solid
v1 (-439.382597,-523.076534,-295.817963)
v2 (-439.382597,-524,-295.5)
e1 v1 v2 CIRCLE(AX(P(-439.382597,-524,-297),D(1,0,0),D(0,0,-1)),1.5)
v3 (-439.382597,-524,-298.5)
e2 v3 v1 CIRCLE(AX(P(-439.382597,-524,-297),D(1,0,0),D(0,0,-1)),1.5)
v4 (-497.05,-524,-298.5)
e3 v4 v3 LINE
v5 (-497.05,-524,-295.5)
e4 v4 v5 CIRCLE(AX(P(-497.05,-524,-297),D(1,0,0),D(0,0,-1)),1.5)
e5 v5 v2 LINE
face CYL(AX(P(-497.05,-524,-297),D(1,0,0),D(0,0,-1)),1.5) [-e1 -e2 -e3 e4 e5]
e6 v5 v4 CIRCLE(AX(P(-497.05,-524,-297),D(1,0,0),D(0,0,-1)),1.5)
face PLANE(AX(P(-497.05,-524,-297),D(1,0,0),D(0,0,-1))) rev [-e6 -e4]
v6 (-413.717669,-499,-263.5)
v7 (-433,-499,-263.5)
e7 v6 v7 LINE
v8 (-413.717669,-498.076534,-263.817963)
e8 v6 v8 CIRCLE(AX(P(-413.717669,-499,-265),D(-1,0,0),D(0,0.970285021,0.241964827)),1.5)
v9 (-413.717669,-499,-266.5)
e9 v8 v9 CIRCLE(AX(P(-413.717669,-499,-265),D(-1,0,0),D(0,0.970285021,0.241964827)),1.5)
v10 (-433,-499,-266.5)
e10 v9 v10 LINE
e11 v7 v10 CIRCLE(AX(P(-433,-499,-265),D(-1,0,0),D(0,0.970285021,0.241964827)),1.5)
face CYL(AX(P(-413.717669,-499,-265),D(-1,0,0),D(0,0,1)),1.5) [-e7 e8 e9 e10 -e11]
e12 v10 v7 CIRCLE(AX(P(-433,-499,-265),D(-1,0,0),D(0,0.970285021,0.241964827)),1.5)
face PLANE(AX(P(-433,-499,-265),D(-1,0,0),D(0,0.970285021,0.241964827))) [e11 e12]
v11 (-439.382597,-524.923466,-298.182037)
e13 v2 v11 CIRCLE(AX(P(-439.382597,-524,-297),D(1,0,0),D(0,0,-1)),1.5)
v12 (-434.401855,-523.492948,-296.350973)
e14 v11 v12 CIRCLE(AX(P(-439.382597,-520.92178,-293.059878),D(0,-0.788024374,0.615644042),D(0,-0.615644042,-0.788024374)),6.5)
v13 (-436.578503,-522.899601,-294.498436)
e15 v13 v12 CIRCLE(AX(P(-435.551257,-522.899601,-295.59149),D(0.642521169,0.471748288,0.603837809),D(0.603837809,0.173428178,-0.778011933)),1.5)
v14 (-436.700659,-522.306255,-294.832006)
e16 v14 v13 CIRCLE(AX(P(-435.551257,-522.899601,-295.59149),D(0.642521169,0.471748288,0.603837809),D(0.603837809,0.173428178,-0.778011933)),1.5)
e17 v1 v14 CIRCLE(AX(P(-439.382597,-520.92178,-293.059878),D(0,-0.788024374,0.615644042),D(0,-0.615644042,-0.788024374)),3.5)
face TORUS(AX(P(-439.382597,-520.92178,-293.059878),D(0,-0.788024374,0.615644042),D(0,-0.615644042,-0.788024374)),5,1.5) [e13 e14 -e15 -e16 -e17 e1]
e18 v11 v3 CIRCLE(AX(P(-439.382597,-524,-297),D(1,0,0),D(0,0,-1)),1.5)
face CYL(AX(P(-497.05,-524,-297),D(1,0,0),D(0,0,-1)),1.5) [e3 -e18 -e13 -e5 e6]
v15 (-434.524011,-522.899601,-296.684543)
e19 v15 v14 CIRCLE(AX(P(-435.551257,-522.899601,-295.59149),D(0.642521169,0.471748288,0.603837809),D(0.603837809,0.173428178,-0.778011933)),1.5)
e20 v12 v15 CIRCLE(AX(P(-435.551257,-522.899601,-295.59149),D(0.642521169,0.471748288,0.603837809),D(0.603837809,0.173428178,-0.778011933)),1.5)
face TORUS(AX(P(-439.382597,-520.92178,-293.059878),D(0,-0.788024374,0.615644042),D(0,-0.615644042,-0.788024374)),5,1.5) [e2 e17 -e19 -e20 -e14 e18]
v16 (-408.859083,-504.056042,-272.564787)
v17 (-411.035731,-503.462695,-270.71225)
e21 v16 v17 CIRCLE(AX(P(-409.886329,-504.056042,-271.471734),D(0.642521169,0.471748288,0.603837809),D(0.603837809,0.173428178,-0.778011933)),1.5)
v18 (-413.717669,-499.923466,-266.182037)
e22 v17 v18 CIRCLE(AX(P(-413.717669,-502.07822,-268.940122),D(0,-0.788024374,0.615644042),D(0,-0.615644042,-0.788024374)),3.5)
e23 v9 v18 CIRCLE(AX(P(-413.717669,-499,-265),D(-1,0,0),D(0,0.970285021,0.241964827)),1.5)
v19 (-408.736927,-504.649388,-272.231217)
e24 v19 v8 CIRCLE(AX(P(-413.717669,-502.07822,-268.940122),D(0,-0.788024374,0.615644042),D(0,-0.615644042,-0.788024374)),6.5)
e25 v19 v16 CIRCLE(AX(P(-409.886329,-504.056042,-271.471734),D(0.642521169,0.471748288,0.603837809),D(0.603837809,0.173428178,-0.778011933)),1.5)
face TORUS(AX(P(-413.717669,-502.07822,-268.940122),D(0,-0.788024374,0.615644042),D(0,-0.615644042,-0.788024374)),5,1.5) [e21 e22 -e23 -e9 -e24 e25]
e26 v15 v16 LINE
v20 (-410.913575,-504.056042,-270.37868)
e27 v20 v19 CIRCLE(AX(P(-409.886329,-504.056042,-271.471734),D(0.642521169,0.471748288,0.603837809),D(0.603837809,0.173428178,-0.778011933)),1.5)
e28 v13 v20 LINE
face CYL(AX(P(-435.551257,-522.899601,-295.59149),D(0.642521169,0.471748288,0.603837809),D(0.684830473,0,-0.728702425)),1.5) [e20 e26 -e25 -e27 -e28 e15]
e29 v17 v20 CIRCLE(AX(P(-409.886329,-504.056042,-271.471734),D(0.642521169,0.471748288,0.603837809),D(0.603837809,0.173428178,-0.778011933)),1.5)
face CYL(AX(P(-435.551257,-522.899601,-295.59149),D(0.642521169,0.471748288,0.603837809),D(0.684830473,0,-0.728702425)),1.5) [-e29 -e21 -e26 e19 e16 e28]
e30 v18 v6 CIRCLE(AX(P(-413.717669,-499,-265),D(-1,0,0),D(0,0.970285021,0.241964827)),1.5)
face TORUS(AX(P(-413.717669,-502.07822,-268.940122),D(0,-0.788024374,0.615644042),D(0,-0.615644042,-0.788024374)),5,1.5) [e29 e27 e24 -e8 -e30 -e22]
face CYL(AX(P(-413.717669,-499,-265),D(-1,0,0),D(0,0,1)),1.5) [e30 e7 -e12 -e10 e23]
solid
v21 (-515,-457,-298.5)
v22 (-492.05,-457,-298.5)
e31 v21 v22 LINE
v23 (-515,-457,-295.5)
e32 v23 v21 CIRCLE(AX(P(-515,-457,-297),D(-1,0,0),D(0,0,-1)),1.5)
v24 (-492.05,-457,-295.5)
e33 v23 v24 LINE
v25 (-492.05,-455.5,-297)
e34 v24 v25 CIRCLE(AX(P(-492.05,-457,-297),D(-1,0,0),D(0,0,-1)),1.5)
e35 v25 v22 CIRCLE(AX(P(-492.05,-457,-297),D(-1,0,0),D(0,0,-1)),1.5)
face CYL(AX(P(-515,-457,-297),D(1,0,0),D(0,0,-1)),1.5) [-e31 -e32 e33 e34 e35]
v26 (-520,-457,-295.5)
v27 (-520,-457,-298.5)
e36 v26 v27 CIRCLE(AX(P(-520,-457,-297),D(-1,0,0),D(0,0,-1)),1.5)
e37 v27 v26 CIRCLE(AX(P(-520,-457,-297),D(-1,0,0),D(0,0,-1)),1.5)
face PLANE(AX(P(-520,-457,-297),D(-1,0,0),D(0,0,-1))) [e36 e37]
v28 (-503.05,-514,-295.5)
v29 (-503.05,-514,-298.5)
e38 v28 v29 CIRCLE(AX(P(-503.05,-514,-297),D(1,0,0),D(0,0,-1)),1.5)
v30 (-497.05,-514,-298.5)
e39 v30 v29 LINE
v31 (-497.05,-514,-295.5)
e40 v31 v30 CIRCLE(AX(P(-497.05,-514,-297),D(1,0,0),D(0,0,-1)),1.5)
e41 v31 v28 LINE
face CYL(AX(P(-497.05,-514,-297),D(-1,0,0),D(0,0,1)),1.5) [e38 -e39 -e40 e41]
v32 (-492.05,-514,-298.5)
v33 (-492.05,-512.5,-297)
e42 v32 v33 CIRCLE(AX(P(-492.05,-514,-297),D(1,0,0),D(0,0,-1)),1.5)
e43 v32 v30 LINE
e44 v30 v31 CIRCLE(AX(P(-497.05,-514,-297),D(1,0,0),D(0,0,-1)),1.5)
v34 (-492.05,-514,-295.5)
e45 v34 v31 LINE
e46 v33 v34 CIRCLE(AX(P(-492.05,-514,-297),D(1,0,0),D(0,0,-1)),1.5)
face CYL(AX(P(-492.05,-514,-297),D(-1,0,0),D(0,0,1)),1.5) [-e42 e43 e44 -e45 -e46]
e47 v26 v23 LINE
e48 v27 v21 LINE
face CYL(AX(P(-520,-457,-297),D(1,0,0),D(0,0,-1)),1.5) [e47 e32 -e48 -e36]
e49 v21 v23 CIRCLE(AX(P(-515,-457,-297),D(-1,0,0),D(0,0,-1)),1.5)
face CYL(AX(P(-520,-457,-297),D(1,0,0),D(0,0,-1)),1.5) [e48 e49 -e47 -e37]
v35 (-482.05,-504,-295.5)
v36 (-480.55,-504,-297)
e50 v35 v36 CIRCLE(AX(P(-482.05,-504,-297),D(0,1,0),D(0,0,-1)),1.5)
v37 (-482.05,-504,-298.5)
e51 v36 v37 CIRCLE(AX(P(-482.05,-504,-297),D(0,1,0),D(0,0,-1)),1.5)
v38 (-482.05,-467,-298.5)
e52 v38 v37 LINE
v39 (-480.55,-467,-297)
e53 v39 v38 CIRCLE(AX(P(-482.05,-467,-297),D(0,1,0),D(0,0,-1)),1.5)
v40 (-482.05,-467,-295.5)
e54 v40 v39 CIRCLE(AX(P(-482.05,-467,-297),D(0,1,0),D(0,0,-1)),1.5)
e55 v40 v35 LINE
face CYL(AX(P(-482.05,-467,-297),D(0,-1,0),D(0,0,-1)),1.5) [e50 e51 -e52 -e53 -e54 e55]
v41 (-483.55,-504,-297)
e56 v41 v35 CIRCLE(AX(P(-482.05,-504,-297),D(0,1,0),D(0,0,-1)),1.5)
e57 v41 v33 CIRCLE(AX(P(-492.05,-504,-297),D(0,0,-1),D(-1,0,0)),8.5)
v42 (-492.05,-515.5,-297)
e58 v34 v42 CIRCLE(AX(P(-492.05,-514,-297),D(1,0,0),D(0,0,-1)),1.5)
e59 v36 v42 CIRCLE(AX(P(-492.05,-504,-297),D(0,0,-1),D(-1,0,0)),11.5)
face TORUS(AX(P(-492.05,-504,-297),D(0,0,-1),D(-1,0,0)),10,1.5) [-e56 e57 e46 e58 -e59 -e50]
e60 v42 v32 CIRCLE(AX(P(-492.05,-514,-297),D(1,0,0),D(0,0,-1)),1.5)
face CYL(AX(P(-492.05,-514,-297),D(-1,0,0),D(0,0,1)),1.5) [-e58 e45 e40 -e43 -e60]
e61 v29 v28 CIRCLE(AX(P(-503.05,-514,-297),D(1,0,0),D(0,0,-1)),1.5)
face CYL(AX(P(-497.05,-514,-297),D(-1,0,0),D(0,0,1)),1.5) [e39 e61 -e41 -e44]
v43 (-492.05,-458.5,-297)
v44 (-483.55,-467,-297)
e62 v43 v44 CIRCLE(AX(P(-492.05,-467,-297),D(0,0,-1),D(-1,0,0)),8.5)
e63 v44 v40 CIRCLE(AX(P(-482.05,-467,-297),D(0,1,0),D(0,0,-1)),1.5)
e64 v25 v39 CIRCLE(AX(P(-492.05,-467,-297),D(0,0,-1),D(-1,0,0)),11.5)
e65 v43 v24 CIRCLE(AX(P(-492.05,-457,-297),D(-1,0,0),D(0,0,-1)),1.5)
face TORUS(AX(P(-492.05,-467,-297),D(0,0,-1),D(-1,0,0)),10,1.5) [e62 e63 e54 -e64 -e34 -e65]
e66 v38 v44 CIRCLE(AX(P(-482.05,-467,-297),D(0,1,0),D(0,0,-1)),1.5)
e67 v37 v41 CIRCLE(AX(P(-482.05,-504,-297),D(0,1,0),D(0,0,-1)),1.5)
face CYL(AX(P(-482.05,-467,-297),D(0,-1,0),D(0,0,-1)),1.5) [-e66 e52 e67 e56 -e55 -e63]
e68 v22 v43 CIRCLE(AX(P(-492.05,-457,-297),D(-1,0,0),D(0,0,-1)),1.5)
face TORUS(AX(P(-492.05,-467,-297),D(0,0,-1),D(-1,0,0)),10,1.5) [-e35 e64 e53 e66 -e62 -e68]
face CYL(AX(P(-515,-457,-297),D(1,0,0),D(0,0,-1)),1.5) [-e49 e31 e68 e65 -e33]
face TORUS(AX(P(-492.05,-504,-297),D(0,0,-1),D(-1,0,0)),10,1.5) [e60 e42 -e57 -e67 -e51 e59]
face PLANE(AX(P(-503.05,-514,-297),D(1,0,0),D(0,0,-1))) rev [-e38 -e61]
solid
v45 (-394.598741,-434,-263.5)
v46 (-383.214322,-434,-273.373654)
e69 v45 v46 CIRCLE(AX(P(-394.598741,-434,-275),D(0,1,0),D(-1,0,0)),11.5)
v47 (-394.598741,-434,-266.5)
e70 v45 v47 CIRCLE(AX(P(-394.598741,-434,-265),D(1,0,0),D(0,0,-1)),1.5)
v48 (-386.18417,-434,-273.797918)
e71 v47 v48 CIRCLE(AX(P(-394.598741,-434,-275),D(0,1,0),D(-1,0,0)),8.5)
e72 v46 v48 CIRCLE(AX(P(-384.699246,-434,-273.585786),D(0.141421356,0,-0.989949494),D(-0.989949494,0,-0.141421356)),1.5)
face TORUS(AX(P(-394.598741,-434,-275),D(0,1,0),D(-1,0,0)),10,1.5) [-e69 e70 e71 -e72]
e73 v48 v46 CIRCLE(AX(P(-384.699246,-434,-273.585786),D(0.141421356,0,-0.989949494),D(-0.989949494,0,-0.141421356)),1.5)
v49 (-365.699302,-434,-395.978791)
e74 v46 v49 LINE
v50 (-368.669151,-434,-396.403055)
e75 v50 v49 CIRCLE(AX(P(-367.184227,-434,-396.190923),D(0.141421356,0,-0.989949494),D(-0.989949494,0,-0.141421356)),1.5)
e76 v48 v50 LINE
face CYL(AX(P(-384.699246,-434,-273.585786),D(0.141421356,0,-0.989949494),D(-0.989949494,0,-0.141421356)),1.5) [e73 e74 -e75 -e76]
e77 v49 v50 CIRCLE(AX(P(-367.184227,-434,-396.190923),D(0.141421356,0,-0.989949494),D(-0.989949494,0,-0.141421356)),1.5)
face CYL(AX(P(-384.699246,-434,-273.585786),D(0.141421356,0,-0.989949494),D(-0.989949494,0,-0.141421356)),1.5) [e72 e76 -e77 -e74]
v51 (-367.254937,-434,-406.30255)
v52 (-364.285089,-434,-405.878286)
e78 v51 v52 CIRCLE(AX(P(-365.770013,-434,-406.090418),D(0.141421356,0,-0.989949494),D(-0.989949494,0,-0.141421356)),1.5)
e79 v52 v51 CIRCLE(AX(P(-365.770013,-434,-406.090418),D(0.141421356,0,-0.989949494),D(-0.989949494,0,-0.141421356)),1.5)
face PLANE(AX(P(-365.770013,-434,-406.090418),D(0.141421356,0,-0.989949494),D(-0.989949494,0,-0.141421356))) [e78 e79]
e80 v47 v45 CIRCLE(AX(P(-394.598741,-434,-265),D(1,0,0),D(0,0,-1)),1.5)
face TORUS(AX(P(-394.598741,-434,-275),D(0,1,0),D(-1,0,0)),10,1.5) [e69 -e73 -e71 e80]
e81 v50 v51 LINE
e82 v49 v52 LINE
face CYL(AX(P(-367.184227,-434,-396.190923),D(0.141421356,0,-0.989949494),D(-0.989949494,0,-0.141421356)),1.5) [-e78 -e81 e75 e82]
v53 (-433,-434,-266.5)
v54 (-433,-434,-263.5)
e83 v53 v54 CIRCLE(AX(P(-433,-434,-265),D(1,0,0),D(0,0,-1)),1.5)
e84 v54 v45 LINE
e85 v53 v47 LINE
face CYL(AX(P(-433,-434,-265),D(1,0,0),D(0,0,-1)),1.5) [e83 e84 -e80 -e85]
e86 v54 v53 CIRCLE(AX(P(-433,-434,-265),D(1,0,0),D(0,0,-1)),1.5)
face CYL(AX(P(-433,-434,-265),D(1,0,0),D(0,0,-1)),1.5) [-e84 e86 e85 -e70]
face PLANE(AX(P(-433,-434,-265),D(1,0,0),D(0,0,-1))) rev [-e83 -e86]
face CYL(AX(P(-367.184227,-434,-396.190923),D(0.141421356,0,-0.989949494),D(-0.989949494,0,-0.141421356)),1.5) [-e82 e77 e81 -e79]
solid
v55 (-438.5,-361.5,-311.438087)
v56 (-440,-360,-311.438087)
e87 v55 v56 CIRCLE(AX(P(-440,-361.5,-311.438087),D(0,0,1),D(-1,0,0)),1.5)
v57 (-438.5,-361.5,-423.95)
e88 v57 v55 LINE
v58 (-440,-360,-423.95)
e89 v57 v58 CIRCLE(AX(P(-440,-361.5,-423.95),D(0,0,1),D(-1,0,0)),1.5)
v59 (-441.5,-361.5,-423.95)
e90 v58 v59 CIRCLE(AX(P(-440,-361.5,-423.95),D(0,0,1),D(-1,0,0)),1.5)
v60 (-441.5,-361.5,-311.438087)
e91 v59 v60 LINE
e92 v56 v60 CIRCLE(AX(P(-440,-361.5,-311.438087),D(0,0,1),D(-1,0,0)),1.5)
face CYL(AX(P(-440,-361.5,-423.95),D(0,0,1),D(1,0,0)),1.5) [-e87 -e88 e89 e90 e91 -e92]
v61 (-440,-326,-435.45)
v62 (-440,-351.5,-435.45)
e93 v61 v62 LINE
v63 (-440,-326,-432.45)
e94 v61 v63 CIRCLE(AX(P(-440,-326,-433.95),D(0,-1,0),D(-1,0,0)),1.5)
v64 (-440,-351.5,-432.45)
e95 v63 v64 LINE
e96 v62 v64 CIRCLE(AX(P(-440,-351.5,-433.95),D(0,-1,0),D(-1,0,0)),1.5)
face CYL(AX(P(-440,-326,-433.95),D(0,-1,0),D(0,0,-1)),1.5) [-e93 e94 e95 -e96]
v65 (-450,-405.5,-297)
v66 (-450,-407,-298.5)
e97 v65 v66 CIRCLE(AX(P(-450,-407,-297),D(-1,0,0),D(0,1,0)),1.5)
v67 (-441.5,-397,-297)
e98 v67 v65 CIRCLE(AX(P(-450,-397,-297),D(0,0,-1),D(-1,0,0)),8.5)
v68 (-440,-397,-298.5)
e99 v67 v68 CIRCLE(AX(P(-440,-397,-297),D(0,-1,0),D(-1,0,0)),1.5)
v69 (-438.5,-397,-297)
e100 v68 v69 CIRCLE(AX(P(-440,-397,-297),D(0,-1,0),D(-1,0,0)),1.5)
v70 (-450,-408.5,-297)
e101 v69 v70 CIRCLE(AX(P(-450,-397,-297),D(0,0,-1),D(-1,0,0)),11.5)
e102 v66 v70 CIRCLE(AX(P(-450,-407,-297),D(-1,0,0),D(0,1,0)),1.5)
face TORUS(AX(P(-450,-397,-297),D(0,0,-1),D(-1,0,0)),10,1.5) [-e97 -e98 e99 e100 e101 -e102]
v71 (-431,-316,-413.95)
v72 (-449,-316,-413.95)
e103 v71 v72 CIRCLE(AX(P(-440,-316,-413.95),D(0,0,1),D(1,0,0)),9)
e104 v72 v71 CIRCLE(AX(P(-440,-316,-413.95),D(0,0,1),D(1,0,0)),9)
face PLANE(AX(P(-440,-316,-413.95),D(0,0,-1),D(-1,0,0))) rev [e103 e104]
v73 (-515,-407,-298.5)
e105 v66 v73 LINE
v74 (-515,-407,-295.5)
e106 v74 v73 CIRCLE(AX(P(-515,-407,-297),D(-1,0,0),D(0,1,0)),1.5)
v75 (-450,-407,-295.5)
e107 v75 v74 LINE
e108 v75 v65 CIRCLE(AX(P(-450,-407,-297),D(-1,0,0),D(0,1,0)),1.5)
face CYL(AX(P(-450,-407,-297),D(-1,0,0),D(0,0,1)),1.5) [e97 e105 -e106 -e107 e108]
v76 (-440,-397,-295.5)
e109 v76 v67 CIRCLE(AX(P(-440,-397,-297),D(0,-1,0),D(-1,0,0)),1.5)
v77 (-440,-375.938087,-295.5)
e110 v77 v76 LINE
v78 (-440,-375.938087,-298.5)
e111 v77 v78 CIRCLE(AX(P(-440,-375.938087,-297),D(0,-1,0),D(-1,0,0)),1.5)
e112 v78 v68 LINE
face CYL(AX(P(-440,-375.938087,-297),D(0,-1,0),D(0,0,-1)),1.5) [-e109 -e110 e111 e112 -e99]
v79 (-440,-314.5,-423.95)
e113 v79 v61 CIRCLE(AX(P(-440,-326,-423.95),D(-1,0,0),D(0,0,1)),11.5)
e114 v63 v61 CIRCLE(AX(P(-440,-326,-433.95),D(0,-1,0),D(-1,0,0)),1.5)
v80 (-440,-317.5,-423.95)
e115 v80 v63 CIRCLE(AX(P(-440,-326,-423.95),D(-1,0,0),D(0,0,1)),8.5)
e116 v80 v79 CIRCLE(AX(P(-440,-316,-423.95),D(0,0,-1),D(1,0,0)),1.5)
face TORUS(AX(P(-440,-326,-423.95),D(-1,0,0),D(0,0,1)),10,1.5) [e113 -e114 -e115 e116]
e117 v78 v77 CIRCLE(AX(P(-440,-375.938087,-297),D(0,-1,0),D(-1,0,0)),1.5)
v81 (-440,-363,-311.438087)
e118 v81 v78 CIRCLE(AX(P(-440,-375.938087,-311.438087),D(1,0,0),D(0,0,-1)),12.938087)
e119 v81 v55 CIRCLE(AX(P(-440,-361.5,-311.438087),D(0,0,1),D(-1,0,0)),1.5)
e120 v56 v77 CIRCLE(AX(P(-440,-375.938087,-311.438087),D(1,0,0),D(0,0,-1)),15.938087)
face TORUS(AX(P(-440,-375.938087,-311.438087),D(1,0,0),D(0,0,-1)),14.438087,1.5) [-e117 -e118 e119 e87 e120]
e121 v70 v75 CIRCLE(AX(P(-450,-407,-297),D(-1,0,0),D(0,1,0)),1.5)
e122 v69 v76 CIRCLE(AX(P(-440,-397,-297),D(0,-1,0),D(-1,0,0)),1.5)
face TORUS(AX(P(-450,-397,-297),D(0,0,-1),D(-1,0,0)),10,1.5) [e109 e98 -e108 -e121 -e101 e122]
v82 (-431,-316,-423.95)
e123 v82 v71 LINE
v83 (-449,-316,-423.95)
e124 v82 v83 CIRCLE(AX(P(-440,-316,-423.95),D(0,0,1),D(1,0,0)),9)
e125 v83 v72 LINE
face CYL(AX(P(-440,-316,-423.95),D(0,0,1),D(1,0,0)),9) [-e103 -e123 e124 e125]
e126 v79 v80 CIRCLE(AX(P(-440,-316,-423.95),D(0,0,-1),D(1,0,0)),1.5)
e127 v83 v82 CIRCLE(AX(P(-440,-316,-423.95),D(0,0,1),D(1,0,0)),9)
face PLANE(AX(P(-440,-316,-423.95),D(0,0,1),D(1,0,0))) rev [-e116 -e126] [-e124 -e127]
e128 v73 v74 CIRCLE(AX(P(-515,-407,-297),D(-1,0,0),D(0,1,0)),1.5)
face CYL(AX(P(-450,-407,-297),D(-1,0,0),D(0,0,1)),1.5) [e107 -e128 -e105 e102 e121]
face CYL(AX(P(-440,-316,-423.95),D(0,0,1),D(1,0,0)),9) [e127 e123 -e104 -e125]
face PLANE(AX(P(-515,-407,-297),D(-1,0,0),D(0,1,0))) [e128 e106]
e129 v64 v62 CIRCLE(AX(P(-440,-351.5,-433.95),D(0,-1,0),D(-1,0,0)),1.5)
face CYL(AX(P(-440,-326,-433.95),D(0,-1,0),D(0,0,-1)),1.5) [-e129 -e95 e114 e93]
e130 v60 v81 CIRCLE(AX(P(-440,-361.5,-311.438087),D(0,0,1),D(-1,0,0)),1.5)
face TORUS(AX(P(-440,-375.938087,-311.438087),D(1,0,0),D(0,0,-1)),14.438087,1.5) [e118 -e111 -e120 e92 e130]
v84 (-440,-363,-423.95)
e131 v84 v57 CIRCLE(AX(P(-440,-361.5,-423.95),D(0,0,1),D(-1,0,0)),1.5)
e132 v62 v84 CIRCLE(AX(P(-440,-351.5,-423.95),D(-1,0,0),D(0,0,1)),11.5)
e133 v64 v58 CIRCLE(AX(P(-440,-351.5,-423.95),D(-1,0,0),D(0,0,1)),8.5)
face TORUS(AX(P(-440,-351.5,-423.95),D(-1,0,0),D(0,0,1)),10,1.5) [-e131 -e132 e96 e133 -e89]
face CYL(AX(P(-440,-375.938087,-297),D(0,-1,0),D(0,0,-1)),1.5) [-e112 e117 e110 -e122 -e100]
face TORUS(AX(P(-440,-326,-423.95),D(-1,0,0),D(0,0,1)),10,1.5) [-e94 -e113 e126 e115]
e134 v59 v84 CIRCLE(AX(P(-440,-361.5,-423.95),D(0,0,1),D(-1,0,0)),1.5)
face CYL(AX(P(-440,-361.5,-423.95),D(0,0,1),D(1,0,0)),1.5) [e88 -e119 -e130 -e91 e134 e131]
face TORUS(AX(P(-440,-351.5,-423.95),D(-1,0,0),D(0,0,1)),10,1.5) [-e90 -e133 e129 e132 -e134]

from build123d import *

# Parameters (mm, degrees)
SWEEP1_PROFILE_R    = 1.5
SWEEP2_PROFILE_R    = 1.5
SWEEP3_PROFILE_R    = 1.5
SWEEP4_PROFILE_R    = 1.5
SKETCH55_R          = 9
BOSS_EXTRUDE1_DEPTH = 10


with BuildPart() as part:
    # Sweep1: sweep along a curve in space
    with BuildLine() as sweep1_path:
        Line((-433, -499, -265), (-413.717668682, -499, -265))
        ThreePointArc((-413.717668682, -499, -265), (-409.186497243, -500.776823058, -267.274333514), (-409.88632901, -504.056041857, -271.471733577))
        Line((-409.88632901, -504.056041857, -271.471733577), (-435.551257158, -522.899601437, -295.59148984))
        ThreePointArc((-435.551257158, -522.899601437, -295.59148984), (-437.268717603, -523.71136849, -296.630551667), (-439.382596831, -524, -297))
        Line((-497.05, -524, -297), (-439.382596831, -524, -297))
    # Sweep1 profile (on start of the path) → Sweep1 (sweep)
    with BuildSketch(Plane(origin=(-433, -499, -265), x_dir=(0, 0, 1), z_dir=(1, 0, 0))):
        Circle(SWEEP1_PROFILE_R)
    sweep(path=sweep1_path.line)


with BuildPart() as body_2:
    # Sweep2: sweep along a path in Sketch2
    with BuildLine(Plane(origin=(0, 0, -297), x_dir=(-1, 0, 0), z_dir=(0, 0, -1))) as sweep2_path:
        Line((520, -457), (515, -457))
        Line((515, -457), (492.05, -457))
        ThreePointArc((492.05, -457), (484.978932188, -459.928932188), (482.05, -467))
        Line((482.05, -467), (482.05, -504))
        ThreePointArc((482.05, -504), (484.978932188, -511.071067812), (492.05, -514))
        Line((492.05, -514), (497.05, -514))
        Line((497.05, -514), (503.05, -514))
    # Sweep2 profile (on start of the path) → Sweep2 (sweep)
    with BuildSketch(Plane(origin=(-520, -457, -297), x_dir=(0, 0, 1), z_dir=(1, 0, 0))):
        Circle(SWEEP2_PROFILE_R)
    sweep(path=sweep2_path.line)


with BuildPart() as body_3:
    # Sweep3: sweep along a path in Sketch1
    with BuildLine(Plane(origin=(0, -434, 0), x_dir=(-1, 0, 0), z_dir=(0, -1, 0))) as sweep3_path:
        Line((365.770013082, 406.090418299), (367.184226644, 396.190923362))
        Line((367.184226644, 396.190923362), (384.699246205, 273.585786438))
        ThreePointArc((384.699246205, 273.585786438), (388.046723728, 267.44546045), (394.598741142, 265))
        Line((394.598741142, 265), (433, 265))
    # Sweep3 profile (on start of the path) → Sweep3 (sweep)
    with BuildSketch(Plane(origin=(-365.770013082, -434, -406.090418299), x_dir=(0.9899494936611664, 0, 0.14142135623731125), z_dir=(-0.14142135623731125, 0, 0.9899494936611664))):
        Circle(SWEEP3_PROFILE_R)
    sweep(path=sweep3_path.line)


with BuildPart() as body_4:
    # Sweep4: sweep along a curve in space
    with BuildLine() as sweep4_path:
        Line((-515, -407, -297), (-450, -407, -297))
        ThreePointArc((-450, -407, -297), (-442.928932188, -404.071067812, -297), (-440, -397, -297))
        Line((-440, -375.938087088, -297), (-440, -397, -297))
        ThreePointArc((-440, -375.938087088, -297), (-440, -365.728817801, -301.228817801), (-440, -361.5, -311.438087088))
        Line((-440, -361.5, -423.95), (-440, -361.5, -311.438087088))
        ThreePointArc((-440, -351.5, -433.95), (-440, -358.571067812, -431.021067812), (-440, -361.5, -423.95))
        Line((-440, -326, -433.95), (-440, -351.5, -433.95))
        ThreePointArc((-440, -326, -433.95), (-440, -318.928932188, -431.021067812), (-440, -316, -423.95))
        Line((-440, -316, -413.95), (-440, -316, -423.95))
    # Sweep4 profile (on start of the path) → Sweep4 (sweep)
    with BuildSketch(Plane(origin=(-515, -407, -297), x_dir=(0, 0, 1), z_dir=(1, 0, 0))):
        Circle(SWEEP4_PROFILE_R)
    sweep(path=sweep4_path.line)

    # Sketch55 → Boss-Extrude1 (add)
    with BuildSketch(Plane.XY.offset(-413.95)):
        with Locations((-440, -316)):
            Circle(SKETCH55_R)
    extrude(amount=-BOSS_EXTRUDE1_DEPTH)


solid = Compound([part.part, body_2.part, body_3.part, body_4.part])
